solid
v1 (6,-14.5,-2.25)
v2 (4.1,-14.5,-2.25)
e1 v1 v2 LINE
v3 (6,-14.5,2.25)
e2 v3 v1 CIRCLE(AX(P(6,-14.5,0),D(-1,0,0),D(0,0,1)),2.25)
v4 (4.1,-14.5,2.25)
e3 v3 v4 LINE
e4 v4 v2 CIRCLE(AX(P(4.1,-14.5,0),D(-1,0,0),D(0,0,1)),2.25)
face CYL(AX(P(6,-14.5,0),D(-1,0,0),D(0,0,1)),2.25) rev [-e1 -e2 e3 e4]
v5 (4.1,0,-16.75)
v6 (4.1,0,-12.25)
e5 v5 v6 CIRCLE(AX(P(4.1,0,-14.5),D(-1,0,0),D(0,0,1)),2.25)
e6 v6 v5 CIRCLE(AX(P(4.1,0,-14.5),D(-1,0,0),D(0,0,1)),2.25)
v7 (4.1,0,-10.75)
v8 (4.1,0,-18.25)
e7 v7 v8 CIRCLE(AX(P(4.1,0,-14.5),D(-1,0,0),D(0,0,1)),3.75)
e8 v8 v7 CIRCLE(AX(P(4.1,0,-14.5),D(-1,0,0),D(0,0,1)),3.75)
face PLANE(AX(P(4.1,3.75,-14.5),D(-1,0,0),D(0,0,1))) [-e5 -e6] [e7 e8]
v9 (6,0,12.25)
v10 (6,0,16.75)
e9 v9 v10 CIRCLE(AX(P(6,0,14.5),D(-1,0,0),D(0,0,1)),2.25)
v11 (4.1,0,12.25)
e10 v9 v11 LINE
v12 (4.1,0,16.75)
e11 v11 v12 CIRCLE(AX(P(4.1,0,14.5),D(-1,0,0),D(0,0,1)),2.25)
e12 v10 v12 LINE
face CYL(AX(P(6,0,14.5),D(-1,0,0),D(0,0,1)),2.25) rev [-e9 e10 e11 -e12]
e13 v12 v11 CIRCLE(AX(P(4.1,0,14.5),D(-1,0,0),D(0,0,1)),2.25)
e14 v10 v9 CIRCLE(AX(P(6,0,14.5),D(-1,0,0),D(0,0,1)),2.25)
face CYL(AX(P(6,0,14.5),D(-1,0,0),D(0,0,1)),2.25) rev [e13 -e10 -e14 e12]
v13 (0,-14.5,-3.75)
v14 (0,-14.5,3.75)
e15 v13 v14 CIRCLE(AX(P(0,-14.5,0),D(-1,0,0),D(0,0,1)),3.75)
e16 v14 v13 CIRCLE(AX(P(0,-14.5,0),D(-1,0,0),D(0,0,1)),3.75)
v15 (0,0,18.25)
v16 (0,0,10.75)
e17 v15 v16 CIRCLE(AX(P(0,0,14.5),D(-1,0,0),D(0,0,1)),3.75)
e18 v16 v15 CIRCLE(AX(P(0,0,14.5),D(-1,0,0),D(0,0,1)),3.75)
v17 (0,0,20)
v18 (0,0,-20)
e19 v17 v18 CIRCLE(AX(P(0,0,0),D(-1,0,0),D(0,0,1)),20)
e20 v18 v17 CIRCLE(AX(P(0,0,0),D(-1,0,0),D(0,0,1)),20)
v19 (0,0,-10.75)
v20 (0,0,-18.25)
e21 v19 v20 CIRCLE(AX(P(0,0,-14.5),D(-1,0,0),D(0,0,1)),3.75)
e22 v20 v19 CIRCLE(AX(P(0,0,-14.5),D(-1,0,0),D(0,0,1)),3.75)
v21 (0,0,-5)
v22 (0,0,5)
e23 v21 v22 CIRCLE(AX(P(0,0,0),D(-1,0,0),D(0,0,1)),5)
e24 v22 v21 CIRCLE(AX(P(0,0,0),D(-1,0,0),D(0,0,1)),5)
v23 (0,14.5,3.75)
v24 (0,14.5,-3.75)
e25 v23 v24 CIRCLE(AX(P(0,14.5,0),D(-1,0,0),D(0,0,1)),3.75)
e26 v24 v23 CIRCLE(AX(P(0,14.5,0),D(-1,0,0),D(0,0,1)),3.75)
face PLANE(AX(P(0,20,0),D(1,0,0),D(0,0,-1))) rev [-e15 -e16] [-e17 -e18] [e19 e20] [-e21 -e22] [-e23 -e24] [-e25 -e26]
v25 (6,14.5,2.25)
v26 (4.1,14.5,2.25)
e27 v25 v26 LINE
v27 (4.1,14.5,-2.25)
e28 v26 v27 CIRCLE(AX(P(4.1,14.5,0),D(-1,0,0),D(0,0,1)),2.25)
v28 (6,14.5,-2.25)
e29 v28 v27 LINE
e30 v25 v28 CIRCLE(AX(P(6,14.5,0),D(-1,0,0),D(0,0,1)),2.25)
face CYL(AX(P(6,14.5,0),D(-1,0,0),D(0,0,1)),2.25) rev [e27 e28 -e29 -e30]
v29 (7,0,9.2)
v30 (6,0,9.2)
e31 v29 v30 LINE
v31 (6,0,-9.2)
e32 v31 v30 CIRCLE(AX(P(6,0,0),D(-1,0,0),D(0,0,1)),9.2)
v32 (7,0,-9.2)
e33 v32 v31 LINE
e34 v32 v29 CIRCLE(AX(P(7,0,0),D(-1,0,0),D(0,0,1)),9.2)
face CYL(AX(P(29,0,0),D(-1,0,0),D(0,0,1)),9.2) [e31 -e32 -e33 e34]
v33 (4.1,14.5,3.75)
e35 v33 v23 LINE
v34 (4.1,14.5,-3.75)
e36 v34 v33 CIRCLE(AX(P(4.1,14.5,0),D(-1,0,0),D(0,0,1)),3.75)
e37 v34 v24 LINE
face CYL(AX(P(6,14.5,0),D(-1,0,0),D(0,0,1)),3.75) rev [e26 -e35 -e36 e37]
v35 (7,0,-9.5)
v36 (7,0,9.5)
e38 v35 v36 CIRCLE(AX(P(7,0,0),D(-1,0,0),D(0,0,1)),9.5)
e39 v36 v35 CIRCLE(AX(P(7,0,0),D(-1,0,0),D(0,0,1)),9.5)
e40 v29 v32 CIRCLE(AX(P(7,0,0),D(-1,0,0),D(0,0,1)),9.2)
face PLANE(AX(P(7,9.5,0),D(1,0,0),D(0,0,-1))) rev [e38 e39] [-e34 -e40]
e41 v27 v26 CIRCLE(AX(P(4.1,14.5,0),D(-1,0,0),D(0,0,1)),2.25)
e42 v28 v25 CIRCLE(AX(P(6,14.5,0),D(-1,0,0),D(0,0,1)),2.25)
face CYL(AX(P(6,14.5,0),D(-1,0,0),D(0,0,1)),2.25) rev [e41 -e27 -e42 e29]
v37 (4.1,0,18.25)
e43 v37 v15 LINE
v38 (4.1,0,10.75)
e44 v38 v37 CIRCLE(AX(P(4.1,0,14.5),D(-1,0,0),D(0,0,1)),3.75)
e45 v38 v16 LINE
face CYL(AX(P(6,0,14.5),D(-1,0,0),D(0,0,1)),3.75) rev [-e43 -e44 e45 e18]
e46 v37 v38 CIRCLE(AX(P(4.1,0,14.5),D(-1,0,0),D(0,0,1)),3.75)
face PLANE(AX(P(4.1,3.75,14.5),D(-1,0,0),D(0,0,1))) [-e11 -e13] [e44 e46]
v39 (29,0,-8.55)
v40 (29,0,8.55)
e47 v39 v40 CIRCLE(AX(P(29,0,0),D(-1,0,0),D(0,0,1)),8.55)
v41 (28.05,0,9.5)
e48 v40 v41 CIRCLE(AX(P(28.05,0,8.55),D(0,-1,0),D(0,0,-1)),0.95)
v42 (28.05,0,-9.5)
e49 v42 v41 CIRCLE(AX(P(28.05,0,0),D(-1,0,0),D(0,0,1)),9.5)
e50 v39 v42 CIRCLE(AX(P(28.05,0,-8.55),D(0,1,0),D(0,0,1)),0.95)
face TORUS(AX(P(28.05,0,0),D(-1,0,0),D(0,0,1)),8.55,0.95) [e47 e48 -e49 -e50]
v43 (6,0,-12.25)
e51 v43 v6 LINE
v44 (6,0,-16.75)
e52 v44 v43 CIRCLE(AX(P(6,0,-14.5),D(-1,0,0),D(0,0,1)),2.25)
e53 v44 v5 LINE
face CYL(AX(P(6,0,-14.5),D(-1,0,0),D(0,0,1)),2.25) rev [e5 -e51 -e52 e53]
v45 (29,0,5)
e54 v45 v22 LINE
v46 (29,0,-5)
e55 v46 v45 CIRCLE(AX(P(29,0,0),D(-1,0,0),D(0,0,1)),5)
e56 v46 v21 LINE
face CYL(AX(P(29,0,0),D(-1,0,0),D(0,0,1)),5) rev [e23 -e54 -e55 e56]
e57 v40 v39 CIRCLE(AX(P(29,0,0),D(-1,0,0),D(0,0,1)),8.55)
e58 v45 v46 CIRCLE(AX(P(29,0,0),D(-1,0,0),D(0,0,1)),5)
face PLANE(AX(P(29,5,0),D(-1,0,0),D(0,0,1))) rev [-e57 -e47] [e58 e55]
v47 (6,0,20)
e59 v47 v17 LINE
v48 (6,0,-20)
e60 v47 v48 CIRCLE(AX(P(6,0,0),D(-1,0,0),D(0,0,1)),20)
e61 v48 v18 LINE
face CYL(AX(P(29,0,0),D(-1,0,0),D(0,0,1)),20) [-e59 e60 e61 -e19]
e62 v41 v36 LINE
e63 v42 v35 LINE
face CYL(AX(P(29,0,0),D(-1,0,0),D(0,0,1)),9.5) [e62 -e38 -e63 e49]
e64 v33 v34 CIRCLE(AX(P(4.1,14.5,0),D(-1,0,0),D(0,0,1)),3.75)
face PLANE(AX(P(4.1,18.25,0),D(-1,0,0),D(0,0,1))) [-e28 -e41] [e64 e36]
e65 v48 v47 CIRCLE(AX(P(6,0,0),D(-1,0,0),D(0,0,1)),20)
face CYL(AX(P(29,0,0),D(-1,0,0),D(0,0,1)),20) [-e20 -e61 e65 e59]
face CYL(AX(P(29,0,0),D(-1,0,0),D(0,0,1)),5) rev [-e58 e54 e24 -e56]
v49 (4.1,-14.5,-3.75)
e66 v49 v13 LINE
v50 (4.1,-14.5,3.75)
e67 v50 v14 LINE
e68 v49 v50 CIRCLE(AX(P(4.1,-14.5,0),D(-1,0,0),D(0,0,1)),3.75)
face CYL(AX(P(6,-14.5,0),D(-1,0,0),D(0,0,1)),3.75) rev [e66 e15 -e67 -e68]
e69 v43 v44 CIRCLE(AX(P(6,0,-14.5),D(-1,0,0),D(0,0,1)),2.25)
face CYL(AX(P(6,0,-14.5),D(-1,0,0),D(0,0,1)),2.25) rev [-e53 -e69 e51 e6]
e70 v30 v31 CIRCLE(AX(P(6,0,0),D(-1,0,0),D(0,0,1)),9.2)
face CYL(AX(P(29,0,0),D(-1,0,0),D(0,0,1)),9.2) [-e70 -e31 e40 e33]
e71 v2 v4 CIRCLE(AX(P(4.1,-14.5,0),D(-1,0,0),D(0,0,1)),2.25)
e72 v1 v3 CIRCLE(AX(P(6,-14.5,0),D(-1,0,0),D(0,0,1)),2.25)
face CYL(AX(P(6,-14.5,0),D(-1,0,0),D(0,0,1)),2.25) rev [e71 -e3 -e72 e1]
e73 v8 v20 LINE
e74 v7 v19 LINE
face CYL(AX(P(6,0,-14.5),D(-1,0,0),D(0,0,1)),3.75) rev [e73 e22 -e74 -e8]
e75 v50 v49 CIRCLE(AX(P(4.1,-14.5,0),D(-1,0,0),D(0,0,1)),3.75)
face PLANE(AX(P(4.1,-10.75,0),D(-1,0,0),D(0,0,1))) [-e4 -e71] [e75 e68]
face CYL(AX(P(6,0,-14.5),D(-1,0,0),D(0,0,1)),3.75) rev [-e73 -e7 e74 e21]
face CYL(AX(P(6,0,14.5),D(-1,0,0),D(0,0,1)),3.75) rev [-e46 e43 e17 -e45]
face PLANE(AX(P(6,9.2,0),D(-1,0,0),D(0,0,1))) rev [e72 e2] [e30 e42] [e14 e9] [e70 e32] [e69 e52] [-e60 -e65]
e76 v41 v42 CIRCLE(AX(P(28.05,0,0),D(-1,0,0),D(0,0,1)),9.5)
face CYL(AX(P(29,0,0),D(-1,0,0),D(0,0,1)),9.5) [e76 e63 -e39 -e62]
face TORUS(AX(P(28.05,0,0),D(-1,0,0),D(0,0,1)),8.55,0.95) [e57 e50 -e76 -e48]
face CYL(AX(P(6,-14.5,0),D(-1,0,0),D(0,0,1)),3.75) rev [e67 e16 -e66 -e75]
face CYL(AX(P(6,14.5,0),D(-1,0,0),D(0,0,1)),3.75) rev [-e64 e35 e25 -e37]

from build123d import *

# Parameters (mm, degrees)
PATTERN_LINEAR_1_COUNT      = 2
PATTERN_LINEAR_1_PITCH      = 20.506096654
PATTERN_LINEAR_1_COUNT_DIR2 = 2
PATTERN_LINEAR_1_PITCH_DIR2 = 20.506096654


with BuildPart() as part:
    # 草图1 → 旋转1 (revolve)
    with BuildSketch(Plane.XY, mode=Mode.PRIVATE) as revolve_1_sk:
        with BuildLine():
            Line((0, 20), (0, 5))
            Line((0, 5), (29, 5))
            Line((29, 5), (29, 8.55))
            ThreePointArc((29, 8.55), (28.721751442, 9.221751442), (28.05, 9.5))
            Line((28.05, 9.5), (7, 9.5))
            Line((7, 9.5), (7, 9.2))
            Line((7, 9.2), (6, 9.2))
            Line((6, 9.2), (6, 20))
            Line((6, 20), (0, 20))
        make_face()
    revolve(revolve_1_sk.sketch.rotate(Axis((29, 0, 0), (-1, 0, 0)), 270), axis=Axis((29, 0, 0), (-1, 0, 0)))

    # 草图2 → 切除-旋转1 (revolve, cut)
    with BuildSketch(Plane.XY, mode=Mode.PRIVATE) as cut_revolve_1_sk:
        Polygon((0, 14.5), (0, 18.25), (4.1, 18.25), (4.1, 16.75), (6, 16.75), (6, 14.5), align=None)
    cut_revolve_1 = revolve(cut_revolve_1_sk.sketch.rotate(Axis((6, 14.5, 0), (-1, 0, 0)), 270), axis=Axis((6, 14.5, 0), (-1, 0, 0)), mode=Mode.SUBTRACT)

    # 阵列(线性)1: Cut-Revolve 1 2 × 2
    with Locations(*[Vector(0, -0.7071067811865475, 0.7071067811865477) * (i * PATTERN_LINEAR_1_PITCH) + Vector(0, -0.7071067811865477, -0.7071067811865474) * (j * PATTERN_LINEAR_1_PITCH_DIR2) for i in range(PATTERN_LINEAR_1_COUNT) for j in range(PATTERN_LINEAR_1_COUNT_DIR2) if (i, j) != (0, 0)]):
        add(cut_revolve_1, mode=Mode.SUBTRACT)


solid = part.part
